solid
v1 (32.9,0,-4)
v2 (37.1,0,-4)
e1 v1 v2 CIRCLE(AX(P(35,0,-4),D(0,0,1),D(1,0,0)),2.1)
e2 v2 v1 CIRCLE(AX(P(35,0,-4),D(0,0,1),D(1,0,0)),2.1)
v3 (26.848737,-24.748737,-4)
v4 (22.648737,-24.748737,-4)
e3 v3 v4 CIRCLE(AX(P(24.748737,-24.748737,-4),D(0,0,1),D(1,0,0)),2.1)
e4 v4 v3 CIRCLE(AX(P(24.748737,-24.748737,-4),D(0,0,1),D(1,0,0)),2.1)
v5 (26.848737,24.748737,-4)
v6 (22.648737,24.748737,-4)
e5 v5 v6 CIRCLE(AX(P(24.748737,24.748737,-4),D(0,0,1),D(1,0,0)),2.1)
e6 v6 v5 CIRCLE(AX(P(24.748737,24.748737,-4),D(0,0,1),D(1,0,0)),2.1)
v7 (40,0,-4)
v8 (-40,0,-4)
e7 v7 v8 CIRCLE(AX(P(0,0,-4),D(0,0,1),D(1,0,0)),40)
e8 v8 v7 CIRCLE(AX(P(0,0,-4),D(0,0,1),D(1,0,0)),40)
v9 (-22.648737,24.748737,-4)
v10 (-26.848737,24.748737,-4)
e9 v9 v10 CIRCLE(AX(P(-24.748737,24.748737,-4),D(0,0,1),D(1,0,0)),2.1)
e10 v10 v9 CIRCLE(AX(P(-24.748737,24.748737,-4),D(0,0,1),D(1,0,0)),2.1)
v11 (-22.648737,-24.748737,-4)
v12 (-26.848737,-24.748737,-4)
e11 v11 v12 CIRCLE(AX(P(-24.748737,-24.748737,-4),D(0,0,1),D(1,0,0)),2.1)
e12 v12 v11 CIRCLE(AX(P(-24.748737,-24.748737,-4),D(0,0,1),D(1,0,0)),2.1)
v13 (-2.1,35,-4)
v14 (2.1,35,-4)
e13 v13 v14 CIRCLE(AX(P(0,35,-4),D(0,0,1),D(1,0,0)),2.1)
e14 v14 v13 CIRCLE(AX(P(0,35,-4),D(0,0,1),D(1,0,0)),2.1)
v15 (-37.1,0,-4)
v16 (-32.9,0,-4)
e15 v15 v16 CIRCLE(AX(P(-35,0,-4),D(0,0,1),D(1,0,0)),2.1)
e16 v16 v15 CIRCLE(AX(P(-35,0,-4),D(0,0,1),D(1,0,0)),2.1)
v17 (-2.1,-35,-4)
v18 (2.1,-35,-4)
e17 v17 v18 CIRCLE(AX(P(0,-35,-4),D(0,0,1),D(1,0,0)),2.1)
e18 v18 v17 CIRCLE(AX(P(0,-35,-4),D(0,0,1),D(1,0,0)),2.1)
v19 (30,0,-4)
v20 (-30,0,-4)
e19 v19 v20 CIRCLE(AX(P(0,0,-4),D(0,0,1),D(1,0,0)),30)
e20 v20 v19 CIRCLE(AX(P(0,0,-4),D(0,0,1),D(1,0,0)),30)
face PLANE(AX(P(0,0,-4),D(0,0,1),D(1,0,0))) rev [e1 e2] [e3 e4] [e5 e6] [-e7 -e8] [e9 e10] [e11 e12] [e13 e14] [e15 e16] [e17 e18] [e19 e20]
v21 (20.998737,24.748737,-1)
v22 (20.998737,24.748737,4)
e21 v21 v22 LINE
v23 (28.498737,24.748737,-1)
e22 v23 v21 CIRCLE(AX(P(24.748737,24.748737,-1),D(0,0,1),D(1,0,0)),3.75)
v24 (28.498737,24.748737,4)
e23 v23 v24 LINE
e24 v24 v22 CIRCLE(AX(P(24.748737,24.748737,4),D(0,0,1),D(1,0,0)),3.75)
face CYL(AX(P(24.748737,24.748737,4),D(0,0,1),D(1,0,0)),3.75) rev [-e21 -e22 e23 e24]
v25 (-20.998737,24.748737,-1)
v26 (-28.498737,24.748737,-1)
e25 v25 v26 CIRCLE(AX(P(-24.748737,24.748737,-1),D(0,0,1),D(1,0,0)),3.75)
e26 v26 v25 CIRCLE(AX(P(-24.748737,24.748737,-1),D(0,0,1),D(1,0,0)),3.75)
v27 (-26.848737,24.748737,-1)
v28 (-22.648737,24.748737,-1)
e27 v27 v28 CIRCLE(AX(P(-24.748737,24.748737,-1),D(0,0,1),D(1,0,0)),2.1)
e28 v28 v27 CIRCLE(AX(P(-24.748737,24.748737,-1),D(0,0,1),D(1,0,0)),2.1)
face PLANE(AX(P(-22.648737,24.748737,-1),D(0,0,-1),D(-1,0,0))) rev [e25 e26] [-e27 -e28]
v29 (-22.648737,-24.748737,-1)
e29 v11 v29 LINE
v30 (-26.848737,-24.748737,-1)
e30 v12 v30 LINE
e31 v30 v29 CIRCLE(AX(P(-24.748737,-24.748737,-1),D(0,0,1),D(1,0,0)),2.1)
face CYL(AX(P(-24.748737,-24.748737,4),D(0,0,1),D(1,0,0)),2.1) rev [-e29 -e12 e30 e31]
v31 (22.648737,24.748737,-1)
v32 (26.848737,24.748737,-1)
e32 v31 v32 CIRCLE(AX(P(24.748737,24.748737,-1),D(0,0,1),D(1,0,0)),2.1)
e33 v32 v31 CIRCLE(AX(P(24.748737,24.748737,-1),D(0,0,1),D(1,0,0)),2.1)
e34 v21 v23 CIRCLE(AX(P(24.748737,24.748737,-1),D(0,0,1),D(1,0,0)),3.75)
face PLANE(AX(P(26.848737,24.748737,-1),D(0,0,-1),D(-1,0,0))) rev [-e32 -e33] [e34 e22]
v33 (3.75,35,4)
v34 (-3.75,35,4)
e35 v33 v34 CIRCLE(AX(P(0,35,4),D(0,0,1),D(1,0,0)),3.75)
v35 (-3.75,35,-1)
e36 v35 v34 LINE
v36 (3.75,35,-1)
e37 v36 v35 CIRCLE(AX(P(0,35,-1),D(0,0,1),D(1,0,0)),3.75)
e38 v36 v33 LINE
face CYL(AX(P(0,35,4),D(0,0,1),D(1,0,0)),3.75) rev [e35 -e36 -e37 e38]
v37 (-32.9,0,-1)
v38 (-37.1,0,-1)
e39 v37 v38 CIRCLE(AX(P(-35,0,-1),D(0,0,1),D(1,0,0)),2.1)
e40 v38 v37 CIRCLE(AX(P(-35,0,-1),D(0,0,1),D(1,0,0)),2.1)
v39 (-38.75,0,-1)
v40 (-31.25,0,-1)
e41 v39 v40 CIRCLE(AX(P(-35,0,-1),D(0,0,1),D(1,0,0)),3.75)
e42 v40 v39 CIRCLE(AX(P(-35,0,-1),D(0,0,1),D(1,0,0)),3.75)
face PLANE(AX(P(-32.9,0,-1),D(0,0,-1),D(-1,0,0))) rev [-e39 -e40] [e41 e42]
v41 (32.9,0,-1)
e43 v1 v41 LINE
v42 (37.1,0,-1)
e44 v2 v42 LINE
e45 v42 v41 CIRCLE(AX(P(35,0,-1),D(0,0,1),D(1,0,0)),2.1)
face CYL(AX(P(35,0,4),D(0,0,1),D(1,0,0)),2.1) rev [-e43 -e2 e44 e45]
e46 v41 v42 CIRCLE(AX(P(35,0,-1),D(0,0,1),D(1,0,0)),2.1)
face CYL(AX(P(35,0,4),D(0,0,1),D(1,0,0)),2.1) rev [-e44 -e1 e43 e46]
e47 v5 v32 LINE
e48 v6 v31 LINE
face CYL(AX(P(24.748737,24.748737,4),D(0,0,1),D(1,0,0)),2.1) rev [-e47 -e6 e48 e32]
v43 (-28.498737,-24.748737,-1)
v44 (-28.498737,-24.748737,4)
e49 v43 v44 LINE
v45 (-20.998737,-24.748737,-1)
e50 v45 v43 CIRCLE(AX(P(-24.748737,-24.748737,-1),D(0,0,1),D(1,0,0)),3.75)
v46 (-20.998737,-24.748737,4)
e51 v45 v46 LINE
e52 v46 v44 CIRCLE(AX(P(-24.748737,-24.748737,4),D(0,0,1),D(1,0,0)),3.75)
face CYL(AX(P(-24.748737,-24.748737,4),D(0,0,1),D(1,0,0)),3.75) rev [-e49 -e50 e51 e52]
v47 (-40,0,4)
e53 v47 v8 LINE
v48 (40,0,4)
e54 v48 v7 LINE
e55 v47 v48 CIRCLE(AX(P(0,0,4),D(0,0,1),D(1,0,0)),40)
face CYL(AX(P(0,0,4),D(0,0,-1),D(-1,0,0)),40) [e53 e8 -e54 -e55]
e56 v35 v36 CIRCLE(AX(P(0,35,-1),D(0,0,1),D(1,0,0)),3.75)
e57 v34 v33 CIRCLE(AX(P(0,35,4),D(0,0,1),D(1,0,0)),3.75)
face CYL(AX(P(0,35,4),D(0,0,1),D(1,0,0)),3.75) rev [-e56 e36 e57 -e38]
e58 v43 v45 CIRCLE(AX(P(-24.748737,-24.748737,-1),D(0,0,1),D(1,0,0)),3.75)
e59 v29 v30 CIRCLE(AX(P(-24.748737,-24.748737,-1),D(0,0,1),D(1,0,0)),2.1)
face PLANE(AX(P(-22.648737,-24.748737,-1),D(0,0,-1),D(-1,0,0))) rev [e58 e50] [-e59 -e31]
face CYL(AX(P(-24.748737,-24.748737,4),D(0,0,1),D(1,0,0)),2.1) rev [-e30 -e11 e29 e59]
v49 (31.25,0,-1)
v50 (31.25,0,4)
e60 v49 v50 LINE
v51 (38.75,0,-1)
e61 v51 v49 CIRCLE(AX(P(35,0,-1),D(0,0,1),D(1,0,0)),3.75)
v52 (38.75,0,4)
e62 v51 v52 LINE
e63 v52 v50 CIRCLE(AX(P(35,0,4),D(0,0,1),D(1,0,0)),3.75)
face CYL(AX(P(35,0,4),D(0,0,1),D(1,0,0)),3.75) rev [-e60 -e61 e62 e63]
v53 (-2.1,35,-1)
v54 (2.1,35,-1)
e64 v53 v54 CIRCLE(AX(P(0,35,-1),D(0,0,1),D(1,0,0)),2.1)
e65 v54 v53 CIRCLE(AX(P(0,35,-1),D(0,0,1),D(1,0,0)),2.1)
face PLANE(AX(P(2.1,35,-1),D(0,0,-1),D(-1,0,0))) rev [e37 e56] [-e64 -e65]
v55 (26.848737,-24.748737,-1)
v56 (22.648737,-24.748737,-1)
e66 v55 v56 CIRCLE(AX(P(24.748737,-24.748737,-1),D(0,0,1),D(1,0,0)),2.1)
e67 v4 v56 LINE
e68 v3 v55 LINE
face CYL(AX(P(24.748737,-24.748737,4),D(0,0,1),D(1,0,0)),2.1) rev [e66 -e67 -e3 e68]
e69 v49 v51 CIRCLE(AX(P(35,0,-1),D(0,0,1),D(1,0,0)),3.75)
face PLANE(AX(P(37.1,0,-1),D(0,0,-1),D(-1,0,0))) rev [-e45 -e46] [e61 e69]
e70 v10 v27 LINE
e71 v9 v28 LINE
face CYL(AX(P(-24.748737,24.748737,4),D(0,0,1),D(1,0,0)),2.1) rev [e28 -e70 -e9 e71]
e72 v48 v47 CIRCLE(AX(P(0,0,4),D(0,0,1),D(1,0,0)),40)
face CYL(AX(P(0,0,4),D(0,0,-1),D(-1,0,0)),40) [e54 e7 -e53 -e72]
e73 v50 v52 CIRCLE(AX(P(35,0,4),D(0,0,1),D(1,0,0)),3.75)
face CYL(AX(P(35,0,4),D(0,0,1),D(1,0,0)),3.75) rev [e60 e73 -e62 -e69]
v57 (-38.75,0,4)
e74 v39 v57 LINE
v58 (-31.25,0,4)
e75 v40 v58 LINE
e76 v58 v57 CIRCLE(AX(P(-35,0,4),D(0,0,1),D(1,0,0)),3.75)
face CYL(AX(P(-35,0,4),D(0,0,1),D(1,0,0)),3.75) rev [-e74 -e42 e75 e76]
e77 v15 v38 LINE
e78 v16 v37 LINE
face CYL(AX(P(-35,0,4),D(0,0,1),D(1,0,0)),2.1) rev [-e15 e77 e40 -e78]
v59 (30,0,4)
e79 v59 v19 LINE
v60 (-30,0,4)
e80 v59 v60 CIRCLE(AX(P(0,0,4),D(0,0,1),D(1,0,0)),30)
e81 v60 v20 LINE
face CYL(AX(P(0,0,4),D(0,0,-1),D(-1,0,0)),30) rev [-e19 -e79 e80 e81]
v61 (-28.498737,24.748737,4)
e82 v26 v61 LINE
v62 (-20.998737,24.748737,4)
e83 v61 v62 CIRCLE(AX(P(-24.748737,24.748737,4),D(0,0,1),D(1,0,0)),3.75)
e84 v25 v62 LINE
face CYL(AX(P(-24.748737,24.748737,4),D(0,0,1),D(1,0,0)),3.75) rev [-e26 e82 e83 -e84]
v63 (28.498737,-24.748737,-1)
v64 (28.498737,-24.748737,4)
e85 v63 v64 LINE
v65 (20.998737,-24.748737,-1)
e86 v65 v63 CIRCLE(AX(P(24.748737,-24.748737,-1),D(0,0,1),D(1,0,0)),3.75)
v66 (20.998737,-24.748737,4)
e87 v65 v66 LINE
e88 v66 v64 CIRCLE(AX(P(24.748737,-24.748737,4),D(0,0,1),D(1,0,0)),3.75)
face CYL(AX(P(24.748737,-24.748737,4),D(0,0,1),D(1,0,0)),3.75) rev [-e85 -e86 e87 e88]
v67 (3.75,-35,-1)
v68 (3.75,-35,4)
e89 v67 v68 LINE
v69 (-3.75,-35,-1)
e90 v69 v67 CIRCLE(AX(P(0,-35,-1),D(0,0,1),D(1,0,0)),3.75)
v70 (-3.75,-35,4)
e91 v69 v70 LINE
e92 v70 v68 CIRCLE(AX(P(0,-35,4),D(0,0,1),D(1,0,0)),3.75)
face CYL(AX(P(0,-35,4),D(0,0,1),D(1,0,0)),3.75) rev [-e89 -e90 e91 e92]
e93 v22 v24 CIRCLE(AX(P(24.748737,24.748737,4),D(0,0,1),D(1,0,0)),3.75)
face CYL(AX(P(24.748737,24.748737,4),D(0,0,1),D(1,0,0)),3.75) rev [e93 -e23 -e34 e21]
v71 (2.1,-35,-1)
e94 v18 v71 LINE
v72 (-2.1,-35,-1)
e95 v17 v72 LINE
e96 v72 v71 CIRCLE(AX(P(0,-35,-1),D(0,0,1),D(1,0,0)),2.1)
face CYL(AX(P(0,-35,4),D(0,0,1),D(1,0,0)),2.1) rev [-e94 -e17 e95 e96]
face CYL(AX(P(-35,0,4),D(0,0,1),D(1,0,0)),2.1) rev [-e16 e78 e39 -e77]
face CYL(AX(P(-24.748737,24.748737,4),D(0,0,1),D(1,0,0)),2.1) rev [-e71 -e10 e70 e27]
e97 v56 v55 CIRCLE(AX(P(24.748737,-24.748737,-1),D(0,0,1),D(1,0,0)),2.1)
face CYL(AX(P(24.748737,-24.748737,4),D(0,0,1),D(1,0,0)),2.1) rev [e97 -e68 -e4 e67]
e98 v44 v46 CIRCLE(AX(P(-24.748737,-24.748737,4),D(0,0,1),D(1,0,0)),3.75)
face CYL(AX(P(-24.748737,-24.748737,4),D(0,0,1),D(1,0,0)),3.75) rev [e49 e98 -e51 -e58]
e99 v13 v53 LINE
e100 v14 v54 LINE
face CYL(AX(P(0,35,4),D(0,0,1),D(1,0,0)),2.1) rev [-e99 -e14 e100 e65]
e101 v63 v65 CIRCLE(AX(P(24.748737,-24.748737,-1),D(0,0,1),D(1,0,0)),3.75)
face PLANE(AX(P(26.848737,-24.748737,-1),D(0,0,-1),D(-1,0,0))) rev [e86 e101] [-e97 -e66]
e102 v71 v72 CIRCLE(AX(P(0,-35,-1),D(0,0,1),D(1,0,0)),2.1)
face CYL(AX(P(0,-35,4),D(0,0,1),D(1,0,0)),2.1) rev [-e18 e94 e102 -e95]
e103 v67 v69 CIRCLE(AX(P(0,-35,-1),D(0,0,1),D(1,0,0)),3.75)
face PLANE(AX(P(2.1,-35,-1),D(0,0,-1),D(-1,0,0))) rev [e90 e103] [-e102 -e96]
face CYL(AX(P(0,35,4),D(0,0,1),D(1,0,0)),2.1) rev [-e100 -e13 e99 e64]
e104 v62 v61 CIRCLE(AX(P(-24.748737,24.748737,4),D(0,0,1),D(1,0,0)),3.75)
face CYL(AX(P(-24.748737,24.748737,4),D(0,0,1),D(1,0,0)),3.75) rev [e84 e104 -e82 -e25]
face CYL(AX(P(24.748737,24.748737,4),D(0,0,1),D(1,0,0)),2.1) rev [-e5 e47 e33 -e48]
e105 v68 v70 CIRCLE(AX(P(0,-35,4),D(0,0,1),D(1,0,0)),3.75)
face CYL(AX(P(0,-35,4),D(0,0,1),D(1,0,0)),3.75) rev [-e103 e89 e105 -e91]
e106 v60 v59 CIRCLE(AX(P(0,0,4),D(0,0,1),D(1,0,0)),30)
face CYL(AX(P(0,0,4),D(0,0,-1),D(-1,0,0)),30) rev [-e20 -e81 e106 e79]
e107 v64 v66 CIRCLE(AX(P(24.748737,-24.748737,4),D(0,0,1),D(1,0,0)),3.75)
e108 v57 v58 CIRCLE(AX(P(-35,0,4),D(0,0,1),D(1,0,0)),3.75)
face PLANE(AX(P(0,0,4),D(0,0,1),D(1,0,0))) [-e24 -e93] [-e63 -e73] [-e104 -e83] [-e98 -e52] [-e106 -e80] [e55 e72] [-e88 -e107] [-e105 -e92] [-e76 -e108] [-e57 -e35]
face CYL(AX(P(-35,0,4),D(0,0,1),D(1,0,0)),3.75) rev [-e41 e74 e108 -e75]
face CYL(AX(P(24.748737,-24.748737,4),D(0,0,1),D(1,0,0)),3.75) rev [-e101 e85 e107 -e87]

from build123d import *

# Parameters (mm, degrees)
SKETCH1_R                                            = 40
SKETCH1_R_2                                          = 30
BOSS_EXTRUDE1_DEPTH                                  = 4
HOLE_SIZE_BY_SOCKET_HEAD_CAP_SCREW_TYPE1_D           = 4.2
HOLE_SIZE_BY_SOCKET_HEAD_CAP_SCREW_TYPE1_CBORE_D     = 7.5
HOLE_SIZE_BY_SOCKET_HEAD_CAP_SCREW_TYPE1_CBORE_DEPTH = 5
CIRPATTERN1_COUNT                                    = 8


with BuildPart() as part:
    # Sketch1 → Boss-Extrude1 (new, symmetric)
    with BuildSketch(Plane.XY):
        Circle(SKETCH1_R)
        Circle(SKETCH1_R_2, mode=Mode.SUBTRACT)
    extrude(amount=BOSS_EXTRUDE1_DEPTH, both=True)

    # Hole Size by Socket Head Cap Screw Type1 (through all)
    with Locations(Plane.XY.offset(4)):
        with Locations((35, 0)):
            hole_size_by_socket_head_cap_screw_type1 = CounterBoreHole(HOLE_SIZE_BY_SOCKET_HEAD_CAP_SCREW_TYPE1_D / 2, HOLE_SIZE_BY_SOCKET_HEAD_CAP_SCREW_TYPE1_CBORE_D / 2, HOLE_SIZE_BY_SOCKET_HEAD_CAP_SCREW_TYPE1_CBORE_DEPTH)

    # CirPattern1: Hole Size by Socket Head Cap Screw Type1 ×8 about axis
    cirpattern1_axis = Axis((0, 0, 0), (0, 0, 1))
    for i in range(1, CIRPATTERN1_COUNT):
        add(hole_size_by_socket_head_cap_screw_type1.rotate(cirpattern1_axis, i * 360 / CIRPATTERN1_COUNT), mode=Mode.SUBTRACT)


solid = part.part
